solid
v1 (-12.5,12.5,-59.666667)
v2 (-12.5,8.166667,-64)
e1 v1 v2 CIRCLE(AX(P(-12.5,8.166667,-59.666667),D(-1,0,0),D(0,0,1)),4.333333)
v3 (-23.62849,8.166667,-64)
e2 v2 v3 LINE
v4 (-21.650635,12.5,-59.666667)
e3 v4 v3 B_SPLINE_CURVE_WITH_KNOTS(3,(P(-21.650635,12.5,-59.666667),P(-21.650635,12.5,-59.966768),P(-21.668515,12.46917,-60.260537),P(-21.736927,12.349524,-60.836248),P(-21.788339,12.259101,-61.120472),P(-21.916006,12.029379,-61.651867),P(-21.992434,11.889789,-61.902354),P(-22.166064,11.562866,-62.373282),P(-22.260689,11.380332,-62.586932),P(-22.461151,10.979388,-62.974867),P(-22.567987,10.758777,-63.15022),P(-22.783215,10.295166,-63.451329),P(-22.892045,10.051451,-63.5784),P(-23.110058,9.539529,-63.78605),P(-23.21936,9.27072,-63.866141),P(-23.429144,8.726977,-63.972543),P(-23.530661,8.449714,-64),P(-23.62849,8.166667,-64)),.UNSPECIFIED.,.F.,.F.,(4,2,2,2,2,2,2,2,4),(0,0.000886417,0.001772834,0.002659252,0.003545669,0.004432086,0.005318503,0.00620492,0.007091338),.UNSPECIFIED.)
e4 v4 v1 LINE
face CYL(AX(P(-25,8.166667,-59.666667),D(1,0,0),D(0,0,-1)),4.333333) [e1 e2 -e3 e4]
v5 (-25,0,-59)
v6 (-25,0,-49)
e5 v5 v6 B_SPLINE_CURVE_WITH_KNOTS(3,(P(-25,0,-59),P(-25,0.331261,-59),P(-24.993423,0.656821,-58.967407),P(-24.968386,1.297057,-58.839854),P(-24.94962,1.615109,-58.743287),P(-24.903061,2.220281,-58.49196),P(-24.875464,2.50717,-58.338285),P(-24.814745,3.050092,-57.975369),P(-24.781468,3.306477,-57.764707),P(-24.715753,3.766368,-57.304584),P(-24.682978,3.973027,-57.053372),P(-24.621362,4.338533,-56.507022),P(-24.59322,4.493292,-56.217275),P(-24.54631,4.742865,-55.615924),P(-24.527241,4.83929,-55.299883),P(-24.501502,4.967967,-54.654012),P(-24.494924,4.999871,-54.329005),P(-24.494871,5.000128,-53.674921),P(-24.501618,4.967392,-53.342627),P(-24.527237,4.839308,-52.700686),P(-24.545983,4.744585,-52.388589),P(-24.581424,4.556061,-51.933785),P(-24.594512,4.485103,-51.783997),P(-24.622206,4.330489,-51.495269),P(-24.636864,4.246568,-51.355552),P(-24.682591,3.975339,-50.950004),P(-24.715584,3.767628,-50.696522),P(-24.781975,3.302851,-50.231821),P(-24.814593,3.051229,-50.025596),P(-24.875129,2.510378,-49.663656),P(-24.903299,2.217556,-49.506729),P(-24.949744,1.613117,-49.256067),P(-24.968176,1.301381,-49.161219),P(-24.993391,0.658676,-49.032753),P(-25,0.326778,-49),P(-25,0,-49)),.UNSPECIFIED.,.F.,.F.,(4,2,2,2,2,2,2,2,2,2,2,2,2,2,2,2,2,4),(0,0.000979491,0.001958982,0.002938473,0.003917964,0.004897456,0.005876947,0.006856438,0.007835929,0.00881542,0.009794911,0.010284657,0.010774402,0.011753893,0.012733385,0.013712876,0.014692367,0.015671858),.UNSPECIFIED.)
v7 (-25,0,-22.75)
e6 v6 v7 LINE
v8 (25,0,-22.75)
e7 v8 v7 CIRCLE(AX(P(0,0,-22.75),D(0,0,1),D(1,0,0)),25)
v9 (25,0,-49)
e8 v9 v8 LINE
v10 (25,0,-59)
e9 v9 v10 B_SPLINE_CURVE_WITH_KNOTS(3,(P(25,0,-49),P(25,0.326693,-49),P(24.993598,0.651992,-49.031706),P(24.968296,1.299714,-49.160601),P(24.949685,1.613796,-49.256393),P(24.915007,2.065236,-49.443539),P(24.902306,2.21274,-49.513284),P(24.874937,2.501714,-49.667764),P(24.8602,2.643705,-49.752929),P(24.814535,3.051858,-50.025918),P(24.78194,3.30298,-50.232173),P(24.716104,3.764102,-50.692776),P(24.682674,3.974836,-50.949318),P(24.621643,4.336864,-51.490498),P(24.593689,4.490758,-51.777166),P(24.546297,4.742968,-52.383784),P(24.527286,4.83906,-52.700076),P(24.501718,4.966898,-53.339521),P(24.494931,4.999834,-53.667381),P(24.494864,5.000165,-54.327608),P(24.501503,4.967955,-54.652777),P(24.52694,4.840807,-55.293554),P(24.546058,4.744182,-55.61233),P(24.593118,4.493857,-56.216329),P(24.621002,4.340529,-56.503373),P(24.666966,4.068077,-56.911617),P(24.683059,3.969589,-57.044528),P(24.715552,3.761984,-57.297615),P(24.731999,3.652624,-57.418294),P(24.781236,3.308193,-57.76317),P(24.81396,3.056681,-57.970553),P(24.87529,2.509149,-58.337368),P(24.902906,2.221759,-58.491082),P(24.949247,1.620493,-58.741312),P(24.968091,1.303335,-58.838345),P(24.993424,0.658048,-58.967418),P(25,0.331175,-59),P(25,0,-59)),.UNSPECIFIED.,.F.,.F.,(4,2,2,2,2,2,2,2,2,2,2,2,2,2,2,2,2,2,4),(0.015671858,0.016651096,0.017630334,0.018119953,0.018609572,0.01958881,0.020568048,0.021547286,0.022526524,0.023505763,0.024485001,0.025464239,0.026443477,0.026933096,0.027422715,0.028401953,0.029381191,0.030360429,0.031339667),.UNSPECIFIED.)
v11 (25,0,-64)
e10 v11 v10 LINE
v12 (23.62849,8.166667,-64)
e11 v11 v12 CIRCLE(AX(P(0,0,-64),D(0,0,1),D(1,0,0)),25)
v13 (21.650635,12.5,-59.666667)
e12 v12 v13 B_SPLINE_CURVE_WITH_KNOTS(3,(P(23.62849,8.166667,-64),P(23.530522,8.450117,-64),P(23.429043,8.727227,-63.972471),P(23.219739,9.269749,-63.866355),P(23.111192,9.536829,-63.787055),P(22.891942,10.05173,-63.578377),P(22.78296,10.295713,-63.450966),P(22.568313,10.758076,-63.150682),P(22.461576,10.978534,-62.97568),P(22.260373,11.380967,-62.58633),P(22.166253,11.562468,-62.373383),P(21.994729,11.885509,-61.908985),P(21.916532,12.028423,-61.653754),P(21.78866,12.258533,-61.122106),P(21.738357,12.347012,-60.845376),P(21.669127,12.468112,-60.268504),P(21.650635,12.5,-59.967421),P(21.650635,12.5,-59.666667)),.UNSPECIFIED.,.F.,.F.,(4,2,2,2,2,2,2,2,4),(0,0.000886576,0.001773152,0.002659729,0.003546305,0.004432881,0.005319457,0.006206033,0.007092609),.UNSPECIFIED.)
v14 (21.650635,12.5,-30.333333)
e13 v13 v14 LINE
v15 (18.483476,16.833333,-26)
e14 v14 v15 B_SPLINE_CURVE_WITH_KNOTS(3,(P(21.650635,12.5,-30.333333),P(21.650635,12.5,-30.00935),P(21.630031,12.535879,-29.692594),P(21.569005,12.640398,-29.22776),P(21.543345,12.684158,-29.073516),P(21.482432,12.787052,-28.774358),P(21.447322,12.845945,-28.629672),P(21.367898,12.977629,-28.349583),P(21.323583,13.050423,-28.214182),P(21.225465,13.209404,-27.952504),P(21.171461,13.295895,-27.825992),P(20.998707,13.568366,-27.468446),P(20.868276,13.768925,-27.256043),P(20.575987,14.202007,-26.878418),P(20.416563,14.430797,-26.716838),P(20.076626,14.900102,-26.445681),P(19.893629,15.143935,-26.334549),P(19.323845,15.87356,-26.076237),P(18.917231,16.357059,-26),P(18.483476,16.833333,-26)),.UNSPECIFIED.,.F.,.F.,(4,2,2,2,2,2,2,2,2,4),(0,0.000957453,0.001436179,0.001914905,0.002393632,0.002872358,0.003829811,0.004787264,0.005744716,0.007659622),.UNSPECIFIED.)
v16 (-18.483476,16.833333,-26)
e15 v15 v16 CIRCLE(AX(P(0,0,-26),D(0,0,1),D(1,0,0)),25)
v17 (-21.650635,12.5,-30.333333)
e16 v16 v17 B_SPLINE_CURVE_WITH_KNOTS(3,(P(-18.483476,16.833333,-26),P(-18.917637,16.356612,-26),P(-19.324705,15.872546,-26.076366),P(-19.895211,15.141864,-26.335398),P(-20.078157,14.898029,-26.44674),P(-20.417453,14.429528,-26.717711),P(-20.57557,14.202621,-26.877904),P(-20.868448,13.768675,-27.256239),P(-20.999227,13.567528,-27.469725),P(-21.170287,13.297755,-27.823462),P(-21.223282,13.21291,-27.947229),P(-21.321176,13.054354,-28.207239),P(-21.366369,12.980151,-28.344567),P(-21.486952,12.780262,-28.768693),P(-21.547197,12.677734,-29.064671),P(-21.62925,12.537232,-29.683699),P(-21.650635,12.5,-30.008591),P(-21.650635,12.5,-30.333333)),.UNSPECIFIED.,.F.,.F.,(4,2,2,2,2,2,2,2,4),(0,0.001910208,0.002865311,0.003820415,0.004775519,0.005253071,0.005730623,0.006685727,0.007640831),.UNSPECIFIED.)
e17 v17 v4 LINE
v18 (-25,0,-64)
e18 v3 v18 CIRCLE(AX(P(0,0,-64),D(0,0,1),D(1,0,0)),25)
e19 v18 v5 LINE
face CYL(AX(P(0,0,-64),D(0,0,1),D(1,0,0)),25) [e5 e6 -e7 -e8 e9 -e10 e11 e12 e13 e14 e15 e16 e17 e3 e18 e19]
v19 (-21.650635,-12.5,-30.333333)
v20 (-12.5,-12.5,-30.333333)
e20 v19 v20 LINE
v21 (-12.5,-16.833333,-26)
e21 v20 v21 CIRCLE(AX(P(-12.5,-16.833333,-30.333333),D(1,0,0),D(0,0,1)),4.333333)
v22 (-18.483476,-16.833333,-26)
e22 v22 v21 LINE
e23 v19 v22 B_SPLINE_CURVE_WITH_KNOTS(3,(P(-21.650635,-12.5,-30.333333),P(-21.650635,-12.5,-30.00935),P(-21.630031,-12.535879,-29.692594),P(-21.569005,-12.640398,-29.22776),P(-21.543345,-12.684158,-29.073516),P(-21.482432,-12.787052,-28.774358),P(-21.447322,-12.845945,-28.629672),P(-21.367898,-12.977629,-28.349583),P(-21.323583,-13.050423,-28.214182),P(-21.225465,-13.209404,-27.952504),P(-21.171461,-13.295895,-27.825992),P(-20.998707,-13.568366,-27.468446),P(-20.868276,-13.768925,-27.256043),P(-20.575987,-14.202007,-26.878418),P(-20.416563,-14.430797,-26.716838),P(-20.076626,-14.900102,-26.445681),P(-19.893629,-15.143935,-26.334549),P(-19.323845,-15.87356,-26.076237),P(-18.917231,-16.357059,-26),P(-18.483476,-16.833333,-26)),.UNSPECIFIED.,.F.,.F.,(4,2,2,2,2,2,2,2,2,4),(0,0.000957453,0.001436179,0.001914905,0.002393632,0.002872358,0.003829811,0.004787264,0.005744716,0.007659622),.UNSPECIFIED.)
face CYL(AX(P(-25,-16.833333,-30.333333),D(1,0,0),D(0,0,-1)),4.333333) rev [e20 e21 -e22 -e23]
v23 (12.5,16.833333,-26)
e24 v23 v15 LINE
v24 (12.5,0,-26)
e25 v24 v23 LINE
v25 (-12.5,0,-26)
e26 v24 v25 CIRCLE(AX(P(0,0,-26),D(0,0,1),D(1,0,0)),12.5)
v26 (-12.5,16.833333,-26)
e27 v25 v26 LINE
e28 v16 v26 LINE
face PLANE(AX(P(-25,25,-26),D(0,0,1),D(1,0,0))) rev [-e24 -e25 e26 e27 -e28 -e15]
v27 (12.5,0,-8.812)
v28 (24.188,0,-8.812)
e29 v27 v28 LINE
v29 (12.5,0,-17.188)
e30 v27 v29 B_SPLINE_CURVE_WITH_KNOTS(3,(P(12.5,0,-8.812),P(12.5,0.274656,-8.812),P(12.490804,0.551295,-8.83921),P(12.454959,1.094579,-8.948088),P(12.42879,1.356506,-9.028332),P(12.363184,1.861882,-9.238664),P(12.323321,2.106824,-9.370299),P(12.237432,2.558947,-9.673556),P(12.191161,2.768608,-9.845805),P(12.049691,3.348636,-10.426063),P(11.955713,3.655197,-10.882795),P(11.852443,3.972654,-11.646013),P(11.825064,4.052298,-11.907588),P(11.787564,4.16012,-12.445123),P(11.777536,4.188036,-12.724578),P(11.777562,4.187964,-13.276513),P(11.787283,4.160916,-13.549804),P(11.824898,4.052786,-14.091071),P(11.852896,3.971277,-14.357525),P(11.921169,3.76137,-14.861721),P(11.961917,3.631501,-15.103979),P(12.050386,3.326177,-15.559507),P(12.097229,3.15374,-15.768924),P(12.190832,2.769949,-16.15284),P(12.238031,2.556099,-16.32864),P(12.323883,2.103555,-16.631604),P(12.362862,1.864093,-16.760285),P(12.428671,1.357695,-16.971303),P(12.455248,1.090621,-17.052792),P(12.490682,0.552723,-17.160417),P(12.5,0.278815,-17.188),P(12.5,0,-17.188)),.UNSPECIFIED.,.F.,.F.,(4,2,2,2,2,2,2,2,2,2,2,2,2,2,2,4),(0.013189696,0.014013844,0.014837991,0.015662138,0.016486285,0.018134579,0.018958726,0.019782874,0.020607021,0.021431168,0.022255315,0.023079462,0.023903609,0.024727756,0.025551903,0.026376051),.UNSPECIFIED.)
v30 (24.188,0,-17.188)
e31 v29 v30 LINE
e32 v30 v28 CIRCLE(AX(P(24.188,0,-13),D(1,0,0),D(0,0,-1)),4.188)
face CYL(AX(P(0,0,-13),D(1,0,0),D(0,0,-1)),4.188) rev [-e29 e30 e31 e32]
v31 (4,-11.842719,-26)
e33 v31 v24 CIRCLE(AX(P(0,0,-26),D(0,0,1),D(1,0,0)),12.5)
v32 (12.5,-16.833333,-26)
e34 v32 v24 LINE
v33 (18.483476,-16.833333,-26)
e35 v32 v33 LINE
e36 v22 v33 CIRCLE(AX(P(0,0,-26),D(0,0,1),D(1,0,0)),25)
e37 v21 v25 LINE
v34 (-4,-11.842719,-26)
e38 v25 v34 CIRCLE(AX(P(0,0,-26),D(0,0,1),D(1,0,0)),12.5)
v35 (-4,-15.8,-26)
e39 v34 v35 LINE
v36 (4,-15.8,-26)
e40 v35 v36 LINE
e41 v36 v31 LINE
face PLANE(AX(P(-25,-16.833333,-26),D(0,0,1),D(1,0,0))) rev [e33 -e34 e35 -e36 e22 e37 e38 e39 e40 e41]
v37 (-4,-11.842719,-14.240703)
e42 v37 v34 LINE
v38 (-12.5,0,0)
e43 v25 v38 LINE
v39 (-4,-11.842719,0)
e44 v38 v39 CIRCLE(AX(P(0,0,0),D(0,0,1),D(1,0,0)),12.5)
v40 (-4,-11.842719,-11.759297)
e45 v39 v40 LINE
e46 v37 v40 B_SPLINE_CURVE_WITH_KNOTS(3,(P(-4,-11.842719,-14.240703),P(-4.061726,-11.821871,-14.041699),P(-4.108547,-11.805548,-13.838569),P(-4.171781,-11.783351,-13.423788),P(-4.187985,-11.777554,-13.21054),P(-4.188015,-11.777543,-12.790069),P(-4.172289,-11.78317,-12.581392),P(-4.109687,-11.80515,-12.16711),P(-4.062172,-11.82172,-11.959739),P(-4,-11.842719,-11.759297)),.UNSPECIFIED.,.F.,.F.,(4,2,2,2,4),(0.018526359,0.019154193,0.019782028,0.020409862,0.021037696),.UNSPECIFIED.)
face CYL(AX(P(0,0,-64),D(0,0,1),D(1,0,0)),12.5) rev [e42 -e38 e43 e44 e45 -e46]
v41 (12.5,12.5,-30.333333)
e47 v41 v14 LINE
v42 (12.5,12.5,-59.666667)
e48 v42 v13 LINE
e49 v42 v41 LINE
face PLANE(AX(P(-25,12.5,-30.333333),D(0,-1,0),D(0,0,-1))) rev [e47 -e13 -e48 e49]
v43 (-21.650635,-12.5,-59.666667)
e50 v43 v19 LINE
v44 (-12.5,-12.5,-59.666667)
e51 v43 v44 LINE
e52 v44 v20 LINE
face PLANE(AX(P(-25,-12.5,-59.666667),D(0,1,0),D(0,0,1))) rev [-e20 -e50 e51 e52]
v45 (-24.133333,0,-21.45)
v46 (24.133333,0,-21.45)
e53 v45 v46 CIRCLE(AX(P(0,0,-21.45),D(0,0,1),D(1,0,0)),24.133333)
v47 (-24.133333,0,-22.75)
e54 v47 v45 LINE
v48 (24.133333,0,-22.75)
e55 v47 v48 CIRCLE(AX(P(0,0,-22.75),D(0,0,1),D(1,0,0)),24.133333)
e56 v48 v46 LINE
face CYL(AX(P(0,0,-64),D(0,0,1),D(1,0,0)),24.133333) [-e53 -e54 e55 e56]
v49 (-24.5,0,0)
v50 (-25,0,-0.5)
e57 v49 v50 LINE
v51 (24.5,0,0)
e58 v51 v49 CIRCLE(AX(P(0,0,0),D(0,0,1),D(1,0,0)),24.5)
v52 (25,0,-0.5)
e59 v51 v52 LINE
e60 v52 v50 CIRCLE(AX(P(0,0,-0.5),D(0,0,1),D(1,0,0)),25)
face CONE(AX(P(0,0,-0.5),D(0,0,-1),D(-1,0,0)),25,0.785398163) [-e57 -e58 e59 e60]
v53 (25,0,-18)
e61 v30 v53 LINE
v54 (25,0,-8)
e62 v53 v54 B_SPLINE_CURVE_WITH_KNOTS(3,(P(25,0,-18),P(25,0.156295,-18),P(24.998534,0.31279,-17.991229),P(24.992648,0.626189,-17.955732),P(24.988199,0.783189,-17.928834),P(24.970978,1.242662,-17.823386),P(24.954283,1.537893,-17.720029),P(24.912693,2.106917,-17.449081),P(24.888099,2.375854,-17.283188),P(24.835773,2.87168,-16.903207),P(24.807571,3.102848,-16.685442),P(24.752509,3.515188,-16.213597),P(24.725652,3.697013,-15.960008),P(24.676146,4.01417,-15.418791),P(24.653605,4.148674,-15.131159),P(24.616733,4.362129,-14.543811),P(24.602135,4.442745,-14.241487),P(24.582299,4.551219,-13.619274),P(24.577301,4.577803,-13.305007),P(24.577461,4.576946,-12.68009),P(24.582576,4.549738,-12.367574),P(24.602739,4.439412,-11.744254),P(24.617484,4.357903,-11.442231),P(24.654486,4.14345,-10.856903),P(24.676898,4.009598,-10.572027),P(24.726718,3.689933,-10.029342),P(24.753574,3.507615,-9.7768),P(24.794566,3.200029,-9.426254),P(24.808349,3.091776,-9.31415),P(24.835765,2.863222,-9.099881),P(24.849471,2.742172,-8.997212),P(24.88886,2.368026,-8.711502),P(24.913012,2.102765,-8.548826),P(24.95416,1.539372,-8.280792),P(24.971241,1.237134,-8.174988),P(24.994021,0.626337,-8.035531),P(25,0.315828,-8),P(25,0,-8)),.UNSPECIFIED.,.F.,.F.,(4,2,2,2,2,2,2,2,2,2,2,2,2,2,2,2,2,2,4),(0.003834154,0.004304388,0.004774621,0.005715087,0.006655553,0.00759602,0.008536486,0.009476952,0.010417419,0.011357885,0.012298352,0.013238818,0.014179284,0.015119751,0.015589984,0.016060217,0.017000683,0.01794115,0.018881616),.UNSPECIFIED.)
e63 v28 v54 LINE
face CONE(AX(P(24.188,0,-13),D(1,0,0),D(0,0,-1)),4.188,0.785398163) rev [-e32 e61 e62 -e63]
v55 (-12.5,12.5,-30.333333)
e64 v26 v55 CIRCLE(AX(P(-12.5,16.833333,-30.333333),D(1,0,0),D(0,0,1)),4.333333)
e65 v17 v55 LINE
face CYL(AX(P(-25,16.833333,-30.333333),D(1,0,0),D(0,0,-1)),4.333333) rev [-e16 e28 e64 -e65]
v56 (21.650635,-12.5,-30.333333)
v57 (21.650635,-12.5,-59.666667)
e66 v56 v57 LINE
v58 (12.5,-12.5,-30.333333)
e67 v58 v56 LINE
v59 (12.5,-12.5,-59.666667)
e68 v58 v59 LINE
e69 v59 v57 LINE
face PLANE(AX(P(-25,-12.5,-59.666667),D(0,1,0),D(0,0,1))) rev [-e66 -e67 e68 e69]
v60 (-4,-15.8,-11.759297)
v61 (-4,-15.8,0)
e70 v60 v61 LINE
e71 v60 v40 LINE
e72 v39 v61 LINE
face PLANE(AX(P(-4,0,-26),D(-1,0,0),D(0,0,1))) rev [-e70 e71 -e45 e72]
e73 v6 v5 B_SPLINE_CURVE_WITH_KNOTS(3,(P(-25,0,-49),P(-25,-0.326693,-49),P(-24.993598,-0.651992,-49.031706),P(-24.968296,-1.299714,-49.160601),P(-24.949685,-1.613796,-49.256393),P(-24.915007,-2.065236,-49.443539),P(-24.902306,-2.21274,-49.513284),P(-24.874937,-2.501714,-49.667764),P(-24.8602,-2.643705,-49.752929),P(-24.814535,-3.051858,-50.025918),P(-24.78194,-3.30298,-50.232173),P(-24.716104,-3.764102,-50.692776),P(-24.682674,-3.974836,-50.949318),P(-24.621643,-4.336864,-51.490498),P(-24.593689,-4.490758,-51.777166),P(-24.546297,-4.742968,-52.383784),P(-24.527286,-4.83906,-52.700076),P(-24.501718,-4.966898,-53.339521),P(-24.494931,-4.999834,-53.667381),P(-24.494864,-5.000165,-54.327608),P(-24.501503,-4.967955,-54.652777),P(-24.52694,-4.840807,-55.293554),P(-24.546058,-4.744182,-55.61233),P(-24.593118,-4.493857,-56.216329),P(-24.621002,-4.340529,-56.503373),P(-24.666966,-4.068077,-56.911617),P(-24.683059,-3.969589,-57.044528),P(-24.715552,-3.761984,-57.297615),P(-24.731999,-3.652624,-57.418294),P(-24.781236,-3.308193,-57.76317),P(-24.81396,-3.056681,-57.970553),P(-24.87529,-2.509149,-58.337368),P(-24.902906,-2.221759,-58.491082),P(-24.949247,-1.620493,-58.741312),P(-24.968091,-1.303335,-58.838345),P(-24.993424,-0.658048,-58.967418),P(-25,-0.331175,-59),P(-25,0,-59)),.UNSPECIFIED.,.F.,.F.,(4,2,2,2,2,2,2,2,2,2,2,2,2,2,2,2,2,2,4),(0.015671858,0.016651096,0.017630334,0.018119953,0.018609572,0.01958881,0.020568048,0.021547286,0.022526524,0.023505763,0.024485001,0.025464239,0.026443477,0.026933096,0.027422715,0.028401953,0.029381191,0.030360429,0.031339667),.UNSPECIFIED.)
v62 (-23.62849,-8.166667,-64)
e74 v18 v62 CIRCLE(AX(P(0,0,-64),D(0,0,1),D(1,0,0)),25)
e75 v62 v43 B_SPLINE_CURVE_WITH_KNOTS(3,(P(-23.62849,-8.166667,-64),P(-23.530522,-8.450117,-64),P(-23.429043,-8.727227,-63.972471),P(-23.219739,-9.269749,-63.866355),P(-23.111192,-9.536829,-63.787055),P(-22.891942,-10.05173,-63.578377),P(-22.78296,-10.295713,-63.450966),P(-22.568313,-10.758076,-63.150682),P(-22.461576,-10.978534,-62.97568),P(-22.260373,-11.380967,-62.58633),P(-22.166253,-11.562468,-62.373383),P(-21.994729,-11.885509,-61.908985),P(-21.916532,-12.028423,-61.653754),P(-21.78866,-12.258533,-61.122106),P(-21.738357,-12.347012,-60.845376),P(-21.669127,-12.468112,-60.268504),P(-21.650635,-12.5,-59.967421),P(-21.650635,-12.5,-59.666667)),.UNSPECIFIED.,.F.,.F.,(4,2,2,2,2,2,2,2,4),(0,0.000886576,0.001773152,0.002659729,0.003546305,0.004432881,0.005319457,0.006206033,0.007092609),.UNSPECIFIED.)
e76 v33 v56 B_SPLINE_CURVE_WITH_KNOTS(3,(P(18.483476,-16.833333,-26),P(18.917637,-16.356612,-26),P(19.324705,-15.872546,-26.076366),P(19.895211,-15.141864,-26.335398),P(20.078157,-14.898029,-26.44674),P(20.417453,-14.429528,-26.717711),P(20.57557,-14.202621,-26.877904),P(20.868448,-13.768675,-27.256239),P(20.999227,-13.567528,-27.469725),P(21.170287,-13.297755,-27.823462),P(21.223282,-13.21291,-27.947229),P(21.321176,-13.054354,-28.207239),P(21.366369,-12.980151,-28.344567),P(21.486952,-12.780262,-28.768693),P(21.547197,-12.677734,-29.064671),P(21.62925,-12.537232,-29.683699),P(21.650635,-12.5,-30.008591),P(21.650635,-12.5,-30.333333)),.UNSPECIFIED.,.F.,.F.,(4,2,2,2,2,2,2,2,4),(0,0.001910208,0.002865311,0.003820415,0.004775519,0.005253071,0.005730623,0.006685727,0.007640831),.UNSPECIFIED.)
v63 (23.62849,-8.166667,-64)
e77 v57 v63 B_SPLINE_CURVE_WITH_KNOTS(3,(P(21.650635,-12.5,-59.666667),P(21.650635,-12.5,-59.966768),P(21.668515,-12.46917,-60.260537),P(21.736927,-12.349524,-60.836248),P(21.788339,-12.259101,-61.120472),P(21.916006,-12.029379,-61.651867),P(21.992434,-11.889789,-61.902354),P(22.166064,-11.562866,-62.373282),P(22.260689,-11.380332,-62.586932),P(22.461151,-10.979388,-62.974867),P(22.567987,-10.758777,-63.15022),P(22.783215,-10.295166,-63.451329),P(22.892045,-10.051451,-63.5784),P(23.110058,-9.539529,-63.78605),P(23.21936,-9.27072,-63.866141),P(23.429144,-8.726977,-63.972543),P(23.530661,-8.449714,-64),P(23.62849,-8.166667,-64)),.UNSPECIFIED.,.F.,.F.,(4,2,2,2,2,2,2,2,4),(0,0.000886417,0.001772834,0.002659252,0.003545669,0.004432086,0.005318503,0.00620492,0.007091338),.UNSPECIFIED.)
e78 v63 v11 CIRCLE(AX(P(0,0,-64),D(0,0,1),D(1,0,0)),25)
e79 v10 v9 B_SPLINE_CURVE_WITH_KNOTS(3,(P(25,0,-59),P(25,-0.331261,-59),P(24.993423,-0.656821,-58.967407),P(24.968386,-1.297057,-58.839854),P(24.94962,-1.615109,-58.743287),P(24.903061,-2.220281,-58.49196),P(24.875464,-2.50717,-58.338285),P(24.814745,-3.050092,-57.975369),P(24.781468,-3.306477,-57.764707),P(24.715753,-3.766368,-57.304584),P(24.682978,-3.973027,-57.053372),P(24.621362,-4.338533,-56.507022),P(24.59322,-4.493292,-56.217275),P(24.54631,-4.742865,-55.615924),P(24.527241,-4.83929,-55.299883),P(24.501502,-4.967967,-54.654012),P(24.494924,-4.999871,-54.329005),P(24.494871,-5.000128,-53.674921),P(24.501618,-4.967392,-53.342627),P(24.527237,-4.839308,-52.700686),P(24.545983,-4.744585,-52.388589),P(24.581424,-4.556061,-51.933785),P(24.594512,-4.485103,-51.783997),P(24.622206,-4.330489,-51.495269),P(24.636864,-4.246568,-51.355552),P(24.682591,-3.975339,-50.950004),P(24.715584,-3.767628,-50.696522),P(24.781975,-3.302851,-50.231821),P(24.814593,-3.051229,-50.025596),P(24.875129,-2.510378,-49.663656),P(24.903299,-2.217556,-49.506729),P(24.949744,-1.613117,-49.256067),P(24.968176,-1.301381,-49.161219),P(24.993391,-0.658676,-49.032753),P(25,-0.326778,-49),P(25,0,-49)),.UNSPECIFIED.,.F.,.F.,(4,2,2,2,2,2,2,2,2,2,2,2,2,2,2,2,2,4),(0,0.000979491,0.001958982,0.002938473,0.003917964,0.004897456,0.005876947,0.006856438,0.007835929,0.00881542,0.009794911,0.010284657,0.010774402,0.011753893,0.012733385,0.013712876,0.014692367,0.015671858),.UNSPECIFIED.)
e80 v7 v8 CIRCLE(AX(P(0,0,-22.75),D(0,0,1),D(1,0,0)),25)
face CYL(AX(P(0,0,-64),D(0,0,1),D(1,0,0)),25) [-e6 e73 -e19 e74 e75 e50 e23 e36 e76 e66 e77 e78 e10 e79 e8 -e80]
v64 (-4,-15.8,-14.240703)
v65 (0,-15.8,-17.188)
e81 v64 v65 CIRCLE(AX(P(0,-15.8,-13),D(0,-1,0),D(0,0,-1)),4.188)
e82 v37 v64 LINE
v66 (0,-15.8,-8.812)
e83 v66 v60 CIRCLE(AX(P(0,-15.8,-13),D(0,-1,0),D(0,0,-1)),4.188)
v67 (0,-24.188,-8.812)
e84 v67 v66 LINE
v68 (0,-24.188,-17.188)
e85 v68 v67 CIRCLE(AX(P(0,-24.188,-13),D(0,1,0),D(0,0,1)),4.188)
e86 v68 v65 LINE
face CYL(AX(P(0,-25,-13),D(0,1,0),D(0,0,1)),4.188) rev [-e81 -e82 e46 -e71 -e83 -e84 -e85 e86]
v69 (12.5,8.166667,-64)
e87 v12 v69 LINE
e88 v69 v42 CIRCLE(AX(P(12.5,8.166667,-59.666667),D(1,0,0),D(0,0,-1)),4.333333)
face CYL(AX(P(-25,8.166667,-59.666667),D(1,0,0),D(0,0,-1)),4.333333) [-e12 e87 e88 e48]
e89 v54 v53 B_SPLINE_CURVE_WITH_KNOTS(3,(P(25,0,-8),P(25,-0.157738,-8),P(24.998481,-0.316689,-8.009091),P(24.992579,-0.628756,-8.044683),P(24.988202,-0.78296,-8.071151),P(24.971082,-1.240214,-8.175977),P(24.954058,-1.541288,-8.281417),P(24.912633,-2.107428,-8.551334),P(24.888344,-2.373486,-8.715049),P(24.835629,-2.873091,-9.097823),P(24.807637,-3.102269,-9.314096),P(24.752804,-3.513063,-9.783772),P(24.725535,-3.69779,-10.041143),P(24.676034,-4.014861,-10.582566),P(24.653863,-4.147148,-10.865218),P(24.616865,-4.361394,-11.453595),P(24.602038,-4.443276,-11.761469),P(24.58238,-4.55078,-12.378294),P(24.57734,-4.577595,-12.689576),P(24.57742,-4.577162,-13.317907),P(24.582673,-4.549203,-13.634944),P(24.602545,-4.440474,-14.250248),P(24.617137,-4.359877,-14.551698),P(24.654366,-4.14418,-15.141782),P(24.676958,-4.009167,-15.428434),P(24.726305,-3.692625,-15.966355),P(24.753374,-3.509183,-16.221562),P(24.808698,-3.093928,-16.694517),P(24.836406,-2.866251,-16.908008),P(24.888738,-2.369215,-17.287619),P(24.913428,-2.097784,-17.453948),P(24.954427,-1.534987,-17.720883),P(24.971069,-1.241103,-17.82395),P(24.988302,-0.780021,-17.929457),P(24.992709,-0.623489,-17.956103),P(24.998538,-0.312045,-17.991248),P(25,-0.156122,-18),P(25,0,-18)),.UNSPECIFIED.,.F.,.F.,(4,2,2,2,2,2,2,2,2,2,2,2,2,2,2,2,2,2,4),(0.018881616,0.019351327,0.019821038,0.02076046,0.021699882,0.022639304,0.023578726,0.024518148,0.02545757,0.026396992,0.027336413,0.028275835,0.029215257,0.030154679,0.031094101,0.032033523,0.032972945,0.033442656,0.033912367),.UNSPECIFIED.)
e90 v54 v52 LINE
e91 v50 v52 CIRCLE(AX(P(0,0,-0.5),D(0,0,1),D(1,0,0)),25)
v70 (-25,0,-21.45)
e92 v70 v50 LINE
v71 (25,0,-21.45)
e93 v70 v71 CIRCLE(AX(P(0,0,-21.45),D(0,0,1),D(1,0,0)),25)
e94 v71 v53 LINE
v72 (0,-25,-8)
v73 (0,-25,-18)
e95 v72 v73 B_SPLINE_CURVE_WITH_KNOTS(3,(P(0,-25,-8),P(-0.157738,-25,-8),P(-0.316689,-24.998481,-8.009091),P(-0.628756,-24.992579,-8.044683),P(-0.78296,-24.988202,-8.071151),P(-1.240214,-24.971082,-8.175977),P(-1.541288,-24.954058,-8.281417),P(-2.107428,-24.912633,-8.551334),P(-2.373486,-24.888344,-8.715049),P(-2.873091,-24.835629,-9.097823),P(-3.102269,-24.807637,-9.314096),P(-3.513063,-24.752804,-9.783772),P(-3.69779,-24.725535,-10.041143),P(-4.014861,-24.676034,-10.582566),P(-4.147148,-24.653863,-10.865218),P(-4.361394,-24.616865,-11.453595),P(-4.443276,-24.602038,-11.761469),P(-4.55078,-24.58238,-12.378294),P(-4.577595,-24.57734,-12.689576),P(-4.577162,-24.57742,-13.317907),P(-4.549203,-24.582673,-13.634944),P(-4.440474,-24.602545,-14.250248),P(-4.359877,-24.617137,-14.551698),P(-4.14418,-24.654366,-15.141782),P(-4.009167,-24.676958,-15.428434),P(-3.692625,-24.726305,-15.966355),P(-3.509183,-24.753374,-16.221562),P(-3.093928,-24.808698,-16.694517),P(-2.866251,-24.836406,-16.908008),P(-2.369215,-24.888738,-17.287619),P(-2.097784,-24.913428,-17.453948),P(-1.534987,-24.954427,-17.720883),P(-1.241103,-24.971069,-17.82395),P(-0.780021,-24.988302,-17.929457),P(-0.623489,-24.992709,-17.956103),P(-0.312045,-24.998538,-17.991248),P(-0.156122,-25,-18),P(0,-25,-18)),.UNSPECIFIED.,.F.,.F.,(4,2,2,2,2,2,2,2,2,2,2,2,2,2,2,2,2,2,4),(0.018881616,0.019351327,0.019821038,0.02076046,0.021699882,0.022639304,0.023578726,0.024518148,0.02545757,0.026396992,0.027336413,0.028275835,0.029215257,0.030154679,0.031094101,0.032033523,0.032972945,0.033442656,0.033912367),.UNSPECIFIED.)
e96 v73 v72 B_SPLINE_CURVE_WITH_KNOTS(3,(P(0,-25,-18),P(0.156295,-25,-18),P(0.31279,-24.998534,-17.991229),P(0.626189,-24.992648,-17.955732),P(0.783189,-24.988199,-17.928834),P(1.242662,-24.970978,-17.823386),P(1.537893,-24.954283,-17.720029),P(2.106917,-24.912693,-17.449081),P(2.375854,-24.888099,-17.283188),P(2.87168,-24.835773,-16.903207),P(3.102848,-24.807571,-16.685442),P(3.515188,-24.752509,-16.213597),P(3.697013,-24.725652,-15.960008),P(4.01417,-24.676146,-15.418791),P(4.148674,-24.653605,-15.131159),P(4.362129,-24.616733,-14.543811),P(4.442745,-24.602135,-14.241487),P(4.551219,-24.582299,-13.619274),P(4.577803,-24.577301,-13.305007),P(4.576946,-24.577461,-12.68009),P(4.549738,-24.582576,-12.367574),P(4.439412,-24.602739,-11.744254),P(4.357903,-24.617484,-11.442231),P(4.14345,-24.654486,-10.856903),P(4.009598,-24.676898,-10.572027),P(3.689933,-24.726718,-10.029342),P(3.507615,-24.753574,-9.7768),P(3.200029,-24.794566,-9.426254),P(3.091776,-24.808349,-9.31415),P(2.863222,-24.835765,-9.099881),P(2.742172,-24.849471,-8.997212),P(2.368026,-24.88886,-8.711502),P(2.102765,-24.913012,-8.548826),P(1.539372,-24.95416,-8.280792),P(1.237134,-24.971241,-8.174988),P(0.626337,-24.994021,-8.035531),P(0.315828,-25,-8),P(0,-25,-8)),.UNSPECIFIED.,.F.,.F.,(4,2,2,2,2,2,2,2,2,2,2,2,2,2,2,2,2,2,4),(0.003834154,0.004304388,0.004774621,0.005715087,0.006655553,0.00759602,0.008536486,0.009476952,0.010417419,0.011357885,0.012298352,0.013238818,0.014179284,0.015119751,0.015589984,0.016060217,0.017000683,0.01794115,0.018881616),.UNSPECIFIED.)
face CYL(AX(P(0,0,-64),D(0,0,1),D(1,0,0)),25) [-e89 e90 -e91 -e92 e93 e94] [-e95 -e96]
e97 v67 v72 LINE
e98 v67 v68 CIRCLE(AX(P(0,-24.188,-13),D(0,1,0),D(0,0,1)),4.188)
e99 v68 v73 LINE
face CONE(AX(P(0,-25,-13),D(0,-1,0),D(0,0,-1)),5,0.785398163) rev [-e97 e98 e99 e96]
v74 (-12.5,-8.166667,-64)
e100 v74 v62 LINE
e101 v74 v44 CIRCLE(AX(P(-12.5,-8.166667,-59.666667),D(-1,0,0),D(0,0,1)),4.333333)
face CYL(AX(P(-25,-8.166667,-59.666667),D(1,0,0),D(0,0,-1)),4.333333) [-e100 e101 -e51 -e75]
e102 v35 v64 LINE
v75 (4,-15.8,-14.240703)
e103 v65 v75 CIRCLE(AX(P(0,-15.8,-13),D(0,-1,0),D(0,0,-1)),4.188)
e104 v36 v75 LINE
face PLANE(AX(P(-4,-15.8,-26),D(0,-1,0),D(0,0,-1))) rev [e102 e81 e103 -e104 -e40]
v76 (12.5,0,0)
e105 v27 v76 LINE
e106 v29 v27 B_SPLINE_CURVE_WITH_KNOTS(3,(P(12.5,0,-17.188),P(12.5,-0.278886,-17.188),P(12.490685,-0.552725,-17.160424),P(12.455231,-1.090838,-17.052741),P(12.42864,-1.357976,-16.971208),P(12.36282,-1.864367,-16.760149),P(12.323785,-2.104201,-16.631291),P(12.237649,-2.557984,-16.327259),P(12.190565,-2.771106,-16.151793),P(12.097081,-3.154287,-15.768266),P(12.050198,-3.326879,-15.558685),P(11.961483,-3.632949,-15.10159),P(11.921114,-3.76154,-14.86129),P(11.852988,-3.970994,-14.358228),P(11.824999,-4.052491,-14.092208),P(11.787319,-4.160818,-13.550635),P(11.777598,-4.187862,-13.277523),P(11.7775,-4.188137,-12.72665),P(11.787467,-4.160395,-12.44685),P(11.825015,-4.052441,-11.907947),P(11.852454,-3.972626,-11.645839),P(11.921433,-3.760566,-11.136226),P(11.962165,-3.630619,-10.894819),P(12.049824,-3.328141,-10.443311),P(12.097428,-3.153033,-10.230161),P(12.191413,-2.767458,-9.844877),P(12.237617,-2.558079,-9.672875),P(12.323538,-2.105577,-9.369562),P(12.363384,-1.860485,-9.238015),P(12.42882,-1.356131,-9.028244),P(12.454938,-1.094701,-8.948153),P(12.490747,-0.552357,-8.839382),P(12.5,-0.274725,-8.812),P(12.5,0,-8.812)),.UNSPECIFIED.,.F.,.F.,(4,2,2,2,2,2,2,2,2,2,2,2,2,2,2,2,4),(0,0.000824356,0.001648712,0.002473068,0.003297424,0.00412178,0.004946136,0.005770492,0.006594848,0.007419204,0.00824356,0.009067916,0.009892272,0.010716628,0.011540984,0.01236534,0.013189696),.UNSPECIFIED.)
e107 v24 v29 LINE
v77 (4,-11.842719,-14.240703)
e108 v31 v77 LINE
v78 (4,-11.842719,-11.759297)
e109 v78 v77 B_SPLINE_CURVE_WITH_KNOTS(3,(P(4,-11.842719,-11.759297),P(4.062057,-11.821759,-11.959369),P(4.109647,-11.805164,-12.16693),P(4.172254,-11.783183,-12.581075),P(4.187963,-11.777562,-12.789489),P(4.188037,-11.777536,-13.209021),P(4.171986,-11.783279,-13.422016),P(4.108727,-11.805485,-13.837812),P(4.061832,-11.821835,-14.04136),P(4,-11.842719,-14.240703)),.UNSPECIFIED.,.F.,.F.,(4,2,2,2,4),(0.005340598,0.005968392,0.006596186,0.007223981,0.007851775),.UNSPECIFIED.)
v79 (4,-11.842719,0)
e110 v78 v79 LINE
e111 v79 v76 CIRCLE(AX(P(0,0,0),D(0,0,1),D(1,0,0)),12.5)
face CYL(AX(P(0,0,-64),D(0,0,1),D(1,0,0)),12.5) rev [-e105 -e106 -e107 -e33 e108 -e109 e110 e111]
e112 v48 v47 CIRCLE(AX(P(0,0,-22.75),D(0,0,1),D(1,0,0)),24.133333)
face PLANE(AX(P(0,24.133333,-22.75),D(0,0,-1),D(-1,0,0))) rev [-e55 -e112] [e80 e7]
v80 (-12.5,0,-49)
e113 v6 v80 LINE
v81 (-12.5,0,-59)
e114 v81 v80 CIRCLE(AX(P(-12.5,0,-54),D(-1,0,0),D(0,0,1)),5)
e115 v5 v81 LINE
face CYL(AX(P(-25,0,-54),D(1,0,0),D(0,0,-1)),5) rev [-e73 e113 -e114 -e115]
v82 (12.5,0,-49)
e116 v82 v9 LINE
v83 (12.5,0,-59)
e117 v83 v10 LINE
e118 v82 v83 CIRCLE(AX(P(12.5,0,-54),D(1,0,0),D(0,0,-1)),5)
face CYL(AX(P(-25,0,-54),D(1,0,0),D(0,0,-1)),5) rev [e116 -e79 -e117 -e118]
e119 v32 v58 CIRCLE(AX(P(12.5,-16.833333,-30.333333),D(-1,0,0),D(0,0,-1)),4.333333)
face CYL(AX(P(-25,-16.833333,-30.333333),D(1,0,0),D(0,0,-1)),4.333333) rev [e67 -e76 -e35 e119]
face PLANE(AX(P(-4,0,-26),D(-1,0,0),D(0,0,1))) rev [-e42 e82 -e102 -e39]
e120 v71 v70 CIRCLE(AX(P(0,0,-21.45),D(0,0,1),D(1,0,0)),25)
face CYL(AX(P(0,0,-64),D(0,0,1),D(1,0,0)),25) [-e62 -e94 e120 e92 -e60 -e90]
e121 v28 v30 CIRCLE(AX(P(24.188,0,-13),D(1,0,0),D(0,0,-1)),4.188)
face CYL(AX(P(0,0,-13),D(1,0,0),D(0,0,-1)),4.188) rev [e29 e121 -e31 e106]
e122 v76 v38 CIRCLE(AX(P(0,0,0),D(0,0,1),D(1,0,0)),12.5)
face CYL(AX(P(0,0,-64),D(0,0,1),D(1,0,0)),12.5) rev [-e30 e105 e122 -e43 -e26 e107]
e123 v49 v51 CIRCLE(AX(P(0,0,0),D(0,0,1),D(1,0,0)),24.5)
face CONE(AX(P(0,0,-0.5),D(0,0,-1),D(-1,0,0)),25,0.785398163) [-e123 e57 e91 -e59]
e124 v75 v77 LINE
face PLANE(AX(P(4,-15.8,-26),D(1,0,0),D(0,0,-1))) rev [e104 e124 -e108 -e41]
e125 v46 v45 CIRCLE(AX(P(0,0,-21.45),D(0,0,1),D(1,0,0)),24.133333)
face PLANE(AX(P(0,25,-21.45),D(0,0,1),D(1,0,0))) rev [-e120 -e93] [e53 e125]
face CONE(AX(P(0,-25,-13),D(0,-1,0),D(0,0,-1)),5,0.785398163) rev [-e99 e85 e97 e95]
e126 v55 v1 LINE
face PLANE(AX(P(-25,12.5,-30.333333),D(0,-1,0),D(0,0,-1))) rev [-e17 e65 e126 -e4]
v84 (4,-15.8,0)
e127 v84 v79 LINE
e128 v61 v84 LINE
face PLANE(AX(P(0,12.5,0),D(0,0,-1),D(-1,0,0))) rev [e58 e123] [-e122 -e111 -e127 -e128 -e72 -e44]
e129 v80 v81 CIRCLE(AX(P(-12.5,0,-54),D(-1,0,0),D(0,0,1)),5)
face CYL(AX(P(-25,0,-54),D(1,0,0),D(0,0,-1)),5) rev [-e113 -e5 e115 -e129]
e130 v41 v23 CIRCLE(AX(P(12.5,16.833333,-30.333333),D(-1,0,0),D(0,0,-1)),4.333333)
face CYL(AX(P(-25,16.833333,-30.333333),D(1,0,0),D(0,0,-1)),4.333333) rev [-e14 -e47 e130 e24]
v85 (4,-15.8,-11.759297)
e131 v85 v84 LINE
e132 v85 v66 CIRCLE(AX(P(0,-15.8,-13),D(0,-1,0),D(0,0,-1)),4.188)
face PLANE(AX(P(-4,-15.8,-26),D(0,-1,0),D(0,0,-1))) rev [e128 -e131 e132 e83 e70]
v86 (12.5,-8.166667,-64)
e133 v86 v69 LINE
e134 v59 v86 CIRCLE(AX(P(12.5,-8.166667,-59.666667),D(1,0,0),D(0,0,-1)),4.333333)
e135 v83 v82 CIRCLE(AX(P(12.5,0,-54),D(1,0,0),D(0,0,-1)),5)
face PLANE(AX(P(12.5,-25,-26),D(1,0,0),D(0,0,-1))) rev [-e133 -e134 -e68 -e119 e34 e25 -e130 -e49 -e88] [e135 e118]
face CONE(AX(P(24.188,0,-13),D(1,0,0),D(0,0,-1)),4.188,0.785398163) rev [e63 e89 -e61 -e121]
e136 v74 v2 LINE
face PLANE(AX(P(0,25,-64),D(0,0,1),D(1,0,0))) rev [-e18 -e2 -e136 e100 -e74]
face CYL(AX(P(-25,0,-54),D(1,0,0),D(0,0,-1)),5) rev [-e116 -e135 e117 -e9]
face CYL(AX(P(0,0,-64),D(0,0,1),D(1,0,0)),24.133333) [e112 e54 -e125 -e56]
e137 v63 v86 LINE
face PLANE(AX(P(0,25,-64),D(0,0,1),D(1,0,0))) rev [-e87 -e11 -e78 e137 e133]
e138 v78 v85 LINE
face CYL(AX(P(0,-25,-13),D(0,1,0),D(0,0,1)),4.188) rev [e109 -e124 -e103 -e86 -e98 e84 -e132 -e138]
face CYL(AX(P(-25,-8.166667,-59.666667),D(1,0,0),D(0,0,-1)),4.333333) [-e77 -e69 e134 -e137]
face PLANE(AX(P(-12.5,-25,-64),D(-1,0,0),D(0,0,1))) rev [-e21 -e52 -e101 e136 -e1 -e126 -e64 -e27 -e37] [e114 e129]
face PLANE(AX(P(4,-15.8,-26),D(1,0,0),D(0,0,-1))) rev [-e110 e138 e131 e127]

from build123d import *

# Parameters (mm, degrees)
CUT_EXTRUDE_1_DEPTH      = 25
CUT_EXTRUDE_1_DEPTH_BACK = 25
CUT_EXTRUDE_2_DEPTH      = 25
CUT_EXTRUDE_2_DEPTH_BACK = 25
SKETCH_3_W               = 25
SKETCH_3_H               = 38
CUT_EXTRUDE_3_DEPTH      = 25
CUT_EXTRUDE_3_DEPTH_BACK = 25
SKETCH_4_R               = 5
SKETCH_7_W               = 8
SKETCH_7_H               = 15.8
CUT_EXTRUDE_4_DEPTH      = 26


with BuildPart() as part:
    # 草图1 → 旋转1 (revolve)
    with BuildSketch(Plane(origin=(0, 0, 0), x_dir=(0, 0, -1), z_dir=(1, 0, 0)), mode=Mode.PRIVATE) as revolve_1_sk:
        Polygon((26, 0), (26, 12.5), (0, 12.5), (0, 24.5), (0.5, 25), (21.45, 25), (21.45, 24.133333333), (22.75, 24.133333333), (22.75, 25), (64, 25), (64, 0), align=None)
    revolve(revolve_1_sk.sketch.rotate(Axis((0, 0, -64), (0, 0, 1)), 270), axis=Axis((0, 0, -64), (0, 0, 1)))

    # 草图2 → 切除-拉伸1 (cut, two sides: drawn at the far end of the back side and taken through both)
    with BuildSketch(Plane(origin=(0, 0, 0), x_dir=(0, 0, -1), z_dir=(1, 0, 0)).offset(-CUT_EXTRUDE_1_DEPTH_BACK)):
        with BuildLine():
            Line((30.333333333, 12.5), (59.666666667, 12.5))
            ThreePointArc((59.666666667, 12.5), (62.730796052, 11.230796052), (64, 8.166666667))
            Line((64, 8.166666667), (64, -8.166666667))
            ThreePointArc((64, -8.166666667), (62.730796052, -11.230796052), (59.666666667, -12.5))
            Line((59.666666667, -12.5), (30.333333333, -12.5))
            ThreePointArc((30.333333333, -12.5), (27.269203948, -13.769203948), (26, -16.833333333))
            Line((26, -16.833333333), (26, -25))
            Line((26, -25), (69, -25))
            Line((69, -25), (69, 25))
            Line((69, 25), (26, 25))
            Line((26, 25), (26, 16.833333333))
            ThreePointArc((26, 16.833333333), (27.269203948, 13.769203948), (30.333333333, 12.5))
        make_face()
    extrude(amount=CUT_EXTRUDE_1_DEPTH + CUT_EXTRUDE_1_DEPTH_BACK, mode=Mode.SUBTRACT)

    # 草图3 → 切除-拉伸2 (cut, two sides: drawn at the far end of the back side and taken through both)
    with BuildSketch(Plane(origin=(0, 0, 0), x_dir=(1, 0, 0), z_dir=(0, 1, 0)).offset(-CUT_EXTRUDE_2_DEPTH_BACK)):
        with Locations((0, 45)):
            Rectangle(SKETCH_3_W, SKETCH_3_H)
    extrude(amount=CUT_EXTRUDE_2_DEPTH + CUT_EXTRUDE_2_DEPTH_BACK, mode=Mode.SUBTRACT)

    # 草图4 → 切除-拉伸3 (cut, two sides: drawn at the far end of the back side and taken through both)
    with BuildSketch(Plane(origin=(0, 0, 0), x_dir=(0, 0, -1), z_dir=(1, 0, 0)).offset(-CUT_EXTRUDE_3_DEPTH_BACK)):
        with Locations((54, 0)):
            Circle(SKETCH_4_R)
    extrude(amount=CUT_EXTRUDE_3_DEPTH + CUT_EXTRUDE_3_DEPTH_BACK, mode=Mode.SUBTRACT)

    # 草图5 → 切除-旋转1 (revolve, cut)
    with BuildSketch(Plane(origin=(0, 0, 0), x_dir=(0, 0, -1), z_dir=(1, 0, 0)), mode=Mode.PRIVATE) as cut_revolve_1_sk:
        Polygon((13, 0), (17.188, 0), (17.188, -24.188), (18, -25), (13, -25), align=None)
    revolve(cut_revolve_1_sk.sketch.rotate(Axis((0, -25, -13), (0, 1, 0)), 180), axis=Axis((0, -25, -13), (0, 1, 0)), mode=Mode.SUBTRACT)

    # 草图6 → 切除-旋转2 (revolve, cut)
    with BuildSketch(Plane(origin=(0, 0, 0), x_dir=(1, 0, 0), z_dir=(0, 1, 0)), mode=Mode.PRIVATE) as cut_revolve_2_sk:
        Polygon((25, 13), (25, 8), (24.188, 8.812), (0, 8.812), (0, 13), align=None)
    revolve(cut_revolve_2_sk.sketch.rotate(Axis((0, 0, -13), (1, 0, 0)), 180), axis=Axis((0, 0, -13), (1, 0, 0)), mode=Mode.SUBTRACT)

    # 草图7 → 切除-拉伸4 (cut)
    with BuildSketch(Plane.XY):
        with Locations((0, -7.9)):
            Rectangle(SKETCH_7_W, SKETCH_7_H)
    extrude(amount=-CUT_EXTRUDE_4_DEPTH, mode=Mode.SUBTRACT)


solid = part.part
